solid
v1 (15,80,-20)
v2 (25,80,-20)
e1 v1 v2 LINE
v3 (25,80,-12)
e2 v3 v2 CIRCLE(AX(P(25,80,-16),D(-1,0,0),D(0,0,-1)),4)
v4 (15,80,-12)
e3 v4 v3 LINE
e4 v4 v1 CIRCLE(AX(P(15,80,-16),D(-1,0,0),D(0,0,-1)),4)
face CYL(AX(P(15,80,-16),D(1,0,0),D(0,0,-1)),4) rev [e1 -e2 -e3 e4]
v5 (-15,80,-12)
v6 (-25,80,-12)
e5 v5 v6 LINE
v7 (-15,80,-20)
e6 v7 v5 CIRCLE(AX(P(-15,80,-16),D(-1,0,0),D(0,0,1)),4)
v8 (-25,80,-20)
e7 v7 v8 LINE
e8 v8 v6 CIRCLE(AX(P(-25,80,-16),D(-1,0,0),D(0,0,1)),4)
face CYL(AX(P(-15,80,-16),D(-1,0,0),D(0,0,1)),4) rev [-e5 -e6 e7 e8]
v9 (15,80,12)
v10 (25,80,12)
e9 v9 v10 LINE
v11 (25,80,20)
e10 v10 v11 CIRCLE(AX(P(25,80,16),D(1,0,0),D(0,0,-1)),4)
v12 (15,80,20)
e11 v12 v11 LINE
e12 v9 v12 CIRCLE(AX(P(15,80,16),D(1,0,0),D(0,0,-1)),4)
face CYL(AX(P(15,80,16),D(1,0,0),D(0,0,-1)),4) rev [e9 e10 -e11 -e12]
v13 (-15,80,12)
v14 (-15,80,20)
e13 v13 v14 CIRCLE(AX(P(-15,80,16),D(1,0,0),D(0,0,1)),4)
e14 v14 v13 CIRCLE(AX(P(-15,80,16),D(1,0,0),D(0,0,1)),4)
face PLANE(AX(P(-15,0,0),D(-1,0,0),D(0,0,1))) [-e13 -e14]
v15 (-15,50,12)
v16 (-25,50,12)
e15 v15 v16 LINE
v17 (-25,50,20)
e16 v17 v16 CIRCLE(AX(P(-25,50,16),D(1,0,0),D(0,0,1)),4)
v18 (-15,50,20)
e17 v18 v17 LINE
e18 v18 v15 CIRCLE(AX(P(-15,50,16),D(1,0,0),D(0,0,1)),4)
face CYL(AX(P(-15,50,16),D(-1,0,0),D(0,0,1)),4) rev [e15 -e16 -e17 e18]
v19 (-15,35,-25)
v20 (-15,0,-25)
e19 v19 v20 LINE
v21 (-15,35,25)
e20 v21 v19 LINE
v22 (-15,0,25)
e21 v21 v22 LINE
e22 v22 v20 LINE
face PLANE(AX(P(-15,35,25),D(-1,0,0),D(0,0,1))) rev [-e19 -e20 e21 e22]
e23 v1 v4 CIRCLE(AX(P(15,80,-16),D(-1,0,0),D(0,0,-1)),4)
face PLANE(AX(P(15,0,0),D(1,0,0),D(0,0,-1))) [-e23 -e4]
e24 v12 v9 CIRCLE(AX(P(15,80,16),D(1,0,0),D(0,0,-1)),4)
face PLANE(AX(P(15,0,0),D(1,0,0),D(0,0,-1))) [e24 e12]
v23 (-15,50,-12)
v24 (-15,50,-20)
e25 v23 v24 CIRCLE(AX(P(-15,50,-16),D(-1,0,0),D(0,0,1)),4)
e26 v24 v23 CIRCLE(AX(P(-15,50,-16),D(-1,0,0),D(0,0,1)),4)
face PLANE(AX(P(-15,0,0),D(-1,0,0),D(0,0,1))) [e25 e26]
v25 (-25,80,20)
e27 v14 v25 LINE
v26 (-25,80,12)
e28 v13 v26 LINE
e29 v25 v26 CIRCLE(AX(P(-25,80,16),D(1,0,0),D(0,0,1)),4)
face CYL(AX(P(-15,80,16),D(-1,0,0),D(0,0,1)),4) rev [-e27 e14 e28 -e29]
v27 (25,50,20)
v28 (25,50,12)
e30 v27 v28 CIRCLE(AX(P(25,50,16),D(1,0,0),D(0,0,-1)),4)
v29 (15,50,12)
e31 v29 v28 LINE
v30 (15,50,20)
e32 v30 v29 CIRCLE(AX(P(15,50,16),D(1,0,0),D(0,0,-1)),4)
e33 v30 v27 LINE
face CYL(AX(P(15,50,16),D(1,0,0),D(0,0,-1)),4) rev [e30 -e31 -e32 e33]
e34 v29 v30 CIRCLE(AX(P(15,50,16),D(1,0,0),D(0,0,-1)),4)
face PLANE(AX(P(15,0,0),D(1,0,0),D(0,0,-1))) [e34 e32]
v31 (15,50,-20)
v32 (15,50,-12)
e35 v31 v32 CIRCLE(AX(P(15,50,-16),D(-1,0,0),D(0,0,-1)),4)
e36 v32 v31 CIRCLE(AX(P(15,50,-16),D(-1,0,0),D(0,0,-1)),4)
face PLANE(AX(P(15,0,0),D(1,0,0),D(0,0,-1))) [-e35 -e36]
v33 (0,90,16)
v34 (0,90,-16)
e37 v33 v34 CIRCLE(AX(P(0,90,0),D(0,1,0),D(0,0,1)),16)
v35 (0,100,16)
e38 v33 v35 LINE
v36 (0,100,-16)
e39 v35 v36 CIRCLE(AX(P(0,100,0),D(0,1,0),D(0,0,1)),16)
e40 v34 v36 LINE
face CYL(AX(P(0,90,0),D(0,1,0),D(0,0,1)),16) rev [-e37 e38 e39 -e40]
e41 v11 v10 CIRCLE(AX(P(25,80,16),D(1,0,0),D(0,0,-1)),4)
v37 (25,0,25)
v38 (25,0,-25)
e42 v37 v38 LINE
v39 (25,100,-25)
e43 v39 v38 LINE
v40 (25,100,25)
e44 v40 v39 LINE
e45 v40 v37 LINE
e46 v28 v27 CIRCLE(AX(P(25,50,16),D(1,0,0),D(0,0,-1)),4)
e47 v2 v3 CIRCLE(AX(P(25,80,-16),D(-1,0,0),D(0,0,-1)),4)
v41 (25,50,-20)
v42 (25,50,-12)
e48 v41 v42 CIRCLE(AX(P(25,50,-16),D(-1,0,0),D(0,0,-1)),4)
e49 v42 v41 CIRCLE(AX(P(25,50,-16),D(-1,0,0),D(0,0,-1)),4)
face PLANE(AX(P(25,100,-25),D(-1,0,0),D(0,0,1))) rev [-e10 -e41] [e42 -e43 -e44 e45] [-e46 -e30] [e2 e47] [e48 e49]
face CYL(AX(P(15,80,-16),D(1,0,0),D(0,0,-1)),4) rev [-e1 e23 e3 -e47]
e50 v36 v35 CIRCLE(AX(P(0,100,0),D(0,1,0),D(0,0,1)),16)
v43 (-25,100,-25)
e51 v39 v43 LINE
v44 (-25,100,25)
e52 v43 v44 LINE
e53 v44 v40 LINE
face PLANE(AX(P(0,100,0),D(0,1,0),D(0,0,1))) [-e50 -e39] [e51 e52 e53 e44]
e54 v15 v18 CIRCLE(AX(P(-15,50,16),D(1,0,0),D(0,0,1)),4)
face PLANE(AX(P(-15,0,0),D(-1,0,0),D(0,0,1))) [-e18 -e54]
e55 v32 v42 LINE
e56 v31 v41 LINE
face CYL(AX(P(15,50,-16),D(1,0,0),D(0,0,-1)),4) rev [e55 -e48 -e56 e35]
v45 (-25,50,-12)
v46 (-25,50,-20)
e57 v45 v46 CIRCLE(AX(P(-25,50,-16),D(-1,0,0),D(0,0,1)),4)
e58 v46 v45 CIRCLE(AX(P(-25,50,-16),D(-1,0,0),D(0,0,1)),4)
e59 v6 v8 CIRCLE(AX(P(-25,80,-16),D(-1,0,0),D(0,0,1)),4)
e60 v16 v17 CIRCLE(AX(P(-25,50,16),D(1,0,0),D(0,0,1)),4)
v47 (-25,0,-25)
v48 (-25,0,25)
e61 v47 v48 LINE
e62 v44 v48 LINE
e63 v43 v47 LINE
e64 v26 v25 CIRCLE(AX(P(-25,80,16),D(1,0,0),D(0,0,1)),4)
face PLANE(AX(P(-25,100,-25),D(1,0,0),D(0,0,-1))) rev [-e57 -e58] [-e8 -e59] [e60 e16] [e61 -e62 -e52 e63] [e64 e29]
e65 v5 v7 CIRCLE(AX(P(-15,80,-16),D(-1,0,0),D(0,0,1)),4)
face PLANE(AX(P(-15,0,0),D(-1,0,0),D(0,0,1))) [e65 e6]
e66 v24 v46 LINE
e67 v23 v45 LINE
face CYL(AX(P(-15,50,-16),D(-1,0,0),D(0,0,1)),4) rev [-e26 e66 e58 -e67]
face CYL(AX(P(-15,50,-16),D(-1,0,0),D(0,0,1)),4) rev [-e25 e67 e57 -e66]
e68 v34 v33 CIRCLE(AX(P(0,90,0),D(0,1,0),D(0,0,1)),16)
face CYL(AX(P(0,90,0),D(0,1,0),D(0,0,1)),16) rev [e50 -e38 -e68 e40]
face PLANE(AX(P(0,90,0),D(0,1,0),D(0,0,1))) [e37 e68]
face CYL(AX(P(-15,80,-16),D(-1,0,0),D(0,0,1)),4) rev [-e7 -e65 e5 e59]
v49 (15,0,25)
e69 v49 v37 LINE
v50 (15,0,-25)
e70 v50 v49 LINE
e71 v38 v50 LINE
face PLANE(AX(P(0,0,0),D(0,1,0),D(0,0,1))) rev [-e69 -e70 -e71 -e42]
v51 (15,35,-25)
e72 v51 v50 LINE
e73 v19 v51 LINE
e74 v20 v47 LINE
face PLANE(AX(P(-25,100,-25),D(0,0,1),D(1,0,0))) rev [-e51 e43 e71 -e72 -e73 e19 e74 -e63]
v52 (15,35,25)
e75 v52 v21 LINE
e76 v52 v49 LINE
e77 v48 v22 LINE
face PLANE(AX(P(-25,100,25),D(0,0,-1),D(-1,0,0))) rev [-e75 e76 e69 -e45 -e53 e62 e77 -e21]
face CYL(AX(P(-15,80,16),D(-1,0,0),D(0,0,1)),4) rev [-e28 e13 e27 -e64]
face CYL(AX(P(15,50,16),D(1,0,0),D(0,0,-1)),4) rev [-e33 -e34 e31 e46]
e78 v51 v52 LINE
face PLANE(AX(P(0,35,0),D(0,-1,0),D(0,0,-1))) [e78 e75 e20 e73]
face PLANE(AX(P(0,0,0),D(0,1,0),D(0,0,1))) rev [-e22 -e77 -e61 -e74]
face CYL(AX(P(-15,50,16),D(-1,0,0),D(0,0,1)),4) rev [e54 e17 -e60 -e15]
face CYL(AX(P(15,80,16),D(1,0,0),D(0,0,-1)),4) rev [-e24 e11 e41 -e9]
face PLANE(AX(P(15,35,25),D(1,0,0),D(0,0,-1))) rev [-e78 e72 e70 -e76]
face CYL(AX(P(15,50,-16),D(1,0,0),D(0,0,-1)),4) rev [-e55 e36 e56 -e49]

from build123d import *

# Parameters (mm, degrees)
SKETCH1_W           = 50
SKETCH1_H           = 50
BOSS_EXTRUDE1_DEPTH = 100
SKETCH4_W           = 30
SKETCH4_H           = 50
CUT_EXTRUDE2_DEPTH  = 35
SKETCH6_R           = 16
CUT_EXTRUDE3_DEPTH  = 10
SKETCH8_R           = 4
CUT_EXTRUDE6_DEPTH  = 10
CUT_EXTRUDE7_START  = -10
SKETCH9_R           = 4
CUT_EXTRUDE7_DEPTH  = 10


with BuildPart() as part:
    # Sketch1 → Boss-Extrude1 (new body)
    with BuildSketch(Plane(origin=(0, 0, 0), x_dir=(1, 0, 0), z_dir=(0, 1, 0))):
        Rectangle(SKETCH1_W, SKETCH1_H)
    extrude(amount=BOSS_EXTRUDE1_DEPTH)

    # Sketch4 → Cut-Extrude2 (cut)
    with BuildSketch(Plane.XZ):
        Rectangle(SKETCH4_W, SKETCH4_H)
    extrude(amount=-CUT_EXTRUDE2_DEPTH, mode=Mode.SUBTRACT)

    # Sketch6 → Cut-Extrude3 (cut)
    with BuildSketch(Plane(origin=(0, 100, 0), x_dir=(1, 0, 0), z_dir=(0, 1, 0))):
        with Locations(Location((0, 0, 0), (0, 0, 270))):
            Circle(SKETCH6_R)
    extrude(amount=-CUT_EXTRUDE3_DEPTH, mode=Mode.SUBTRACT)

    # Sketch8 → Cut-Extrude6 (cut)
    with BuildSketch(Plane.ZY.offset(25)):
        with Locations((-16, 80)):
            Circle(SKETCH8_R)
        with Locations((16, 80)):
            Circle(SKETCH8_R)
        with Locations((16, 50)):
            Circle(SKETCH8_R)
        with Locations((-16, 50)):
            Circle(SKETCH8_R)
    extrude(amount=-CUT_EXTRUDE6_DEPTH, mode=Mode.SUBTRACT)

    # Sketch9 → Cut-Extrude7 (cut)
    with BuildSketch(Plane(origin=(25, 0, 0), x_dir=(0, 0, -1), z_dir=(1, 0, 0)).offset(CUT_EXTRUDE7_START)):
        with Locations(Location((-16, 80, 0), (0, 0, 180))):
            Circle(SKETCH9_R)
        with Locations(Location((-16, 50, 0), (0, 0, 180))):
            Circle(SKETCH9_R)
        with Locations(Location((16, 50, 0), (0, 0, 180))):
            Circle(SKETCH9_R)
        with Locations(Location((16, 80, 0), (0, 0, 180))):
            Circle(SKETCH9_R)
    extrude(amount=CUT_EXTRUDE7_DEPTH, mode=Mode.SUBTRACT)


solid = part.part
